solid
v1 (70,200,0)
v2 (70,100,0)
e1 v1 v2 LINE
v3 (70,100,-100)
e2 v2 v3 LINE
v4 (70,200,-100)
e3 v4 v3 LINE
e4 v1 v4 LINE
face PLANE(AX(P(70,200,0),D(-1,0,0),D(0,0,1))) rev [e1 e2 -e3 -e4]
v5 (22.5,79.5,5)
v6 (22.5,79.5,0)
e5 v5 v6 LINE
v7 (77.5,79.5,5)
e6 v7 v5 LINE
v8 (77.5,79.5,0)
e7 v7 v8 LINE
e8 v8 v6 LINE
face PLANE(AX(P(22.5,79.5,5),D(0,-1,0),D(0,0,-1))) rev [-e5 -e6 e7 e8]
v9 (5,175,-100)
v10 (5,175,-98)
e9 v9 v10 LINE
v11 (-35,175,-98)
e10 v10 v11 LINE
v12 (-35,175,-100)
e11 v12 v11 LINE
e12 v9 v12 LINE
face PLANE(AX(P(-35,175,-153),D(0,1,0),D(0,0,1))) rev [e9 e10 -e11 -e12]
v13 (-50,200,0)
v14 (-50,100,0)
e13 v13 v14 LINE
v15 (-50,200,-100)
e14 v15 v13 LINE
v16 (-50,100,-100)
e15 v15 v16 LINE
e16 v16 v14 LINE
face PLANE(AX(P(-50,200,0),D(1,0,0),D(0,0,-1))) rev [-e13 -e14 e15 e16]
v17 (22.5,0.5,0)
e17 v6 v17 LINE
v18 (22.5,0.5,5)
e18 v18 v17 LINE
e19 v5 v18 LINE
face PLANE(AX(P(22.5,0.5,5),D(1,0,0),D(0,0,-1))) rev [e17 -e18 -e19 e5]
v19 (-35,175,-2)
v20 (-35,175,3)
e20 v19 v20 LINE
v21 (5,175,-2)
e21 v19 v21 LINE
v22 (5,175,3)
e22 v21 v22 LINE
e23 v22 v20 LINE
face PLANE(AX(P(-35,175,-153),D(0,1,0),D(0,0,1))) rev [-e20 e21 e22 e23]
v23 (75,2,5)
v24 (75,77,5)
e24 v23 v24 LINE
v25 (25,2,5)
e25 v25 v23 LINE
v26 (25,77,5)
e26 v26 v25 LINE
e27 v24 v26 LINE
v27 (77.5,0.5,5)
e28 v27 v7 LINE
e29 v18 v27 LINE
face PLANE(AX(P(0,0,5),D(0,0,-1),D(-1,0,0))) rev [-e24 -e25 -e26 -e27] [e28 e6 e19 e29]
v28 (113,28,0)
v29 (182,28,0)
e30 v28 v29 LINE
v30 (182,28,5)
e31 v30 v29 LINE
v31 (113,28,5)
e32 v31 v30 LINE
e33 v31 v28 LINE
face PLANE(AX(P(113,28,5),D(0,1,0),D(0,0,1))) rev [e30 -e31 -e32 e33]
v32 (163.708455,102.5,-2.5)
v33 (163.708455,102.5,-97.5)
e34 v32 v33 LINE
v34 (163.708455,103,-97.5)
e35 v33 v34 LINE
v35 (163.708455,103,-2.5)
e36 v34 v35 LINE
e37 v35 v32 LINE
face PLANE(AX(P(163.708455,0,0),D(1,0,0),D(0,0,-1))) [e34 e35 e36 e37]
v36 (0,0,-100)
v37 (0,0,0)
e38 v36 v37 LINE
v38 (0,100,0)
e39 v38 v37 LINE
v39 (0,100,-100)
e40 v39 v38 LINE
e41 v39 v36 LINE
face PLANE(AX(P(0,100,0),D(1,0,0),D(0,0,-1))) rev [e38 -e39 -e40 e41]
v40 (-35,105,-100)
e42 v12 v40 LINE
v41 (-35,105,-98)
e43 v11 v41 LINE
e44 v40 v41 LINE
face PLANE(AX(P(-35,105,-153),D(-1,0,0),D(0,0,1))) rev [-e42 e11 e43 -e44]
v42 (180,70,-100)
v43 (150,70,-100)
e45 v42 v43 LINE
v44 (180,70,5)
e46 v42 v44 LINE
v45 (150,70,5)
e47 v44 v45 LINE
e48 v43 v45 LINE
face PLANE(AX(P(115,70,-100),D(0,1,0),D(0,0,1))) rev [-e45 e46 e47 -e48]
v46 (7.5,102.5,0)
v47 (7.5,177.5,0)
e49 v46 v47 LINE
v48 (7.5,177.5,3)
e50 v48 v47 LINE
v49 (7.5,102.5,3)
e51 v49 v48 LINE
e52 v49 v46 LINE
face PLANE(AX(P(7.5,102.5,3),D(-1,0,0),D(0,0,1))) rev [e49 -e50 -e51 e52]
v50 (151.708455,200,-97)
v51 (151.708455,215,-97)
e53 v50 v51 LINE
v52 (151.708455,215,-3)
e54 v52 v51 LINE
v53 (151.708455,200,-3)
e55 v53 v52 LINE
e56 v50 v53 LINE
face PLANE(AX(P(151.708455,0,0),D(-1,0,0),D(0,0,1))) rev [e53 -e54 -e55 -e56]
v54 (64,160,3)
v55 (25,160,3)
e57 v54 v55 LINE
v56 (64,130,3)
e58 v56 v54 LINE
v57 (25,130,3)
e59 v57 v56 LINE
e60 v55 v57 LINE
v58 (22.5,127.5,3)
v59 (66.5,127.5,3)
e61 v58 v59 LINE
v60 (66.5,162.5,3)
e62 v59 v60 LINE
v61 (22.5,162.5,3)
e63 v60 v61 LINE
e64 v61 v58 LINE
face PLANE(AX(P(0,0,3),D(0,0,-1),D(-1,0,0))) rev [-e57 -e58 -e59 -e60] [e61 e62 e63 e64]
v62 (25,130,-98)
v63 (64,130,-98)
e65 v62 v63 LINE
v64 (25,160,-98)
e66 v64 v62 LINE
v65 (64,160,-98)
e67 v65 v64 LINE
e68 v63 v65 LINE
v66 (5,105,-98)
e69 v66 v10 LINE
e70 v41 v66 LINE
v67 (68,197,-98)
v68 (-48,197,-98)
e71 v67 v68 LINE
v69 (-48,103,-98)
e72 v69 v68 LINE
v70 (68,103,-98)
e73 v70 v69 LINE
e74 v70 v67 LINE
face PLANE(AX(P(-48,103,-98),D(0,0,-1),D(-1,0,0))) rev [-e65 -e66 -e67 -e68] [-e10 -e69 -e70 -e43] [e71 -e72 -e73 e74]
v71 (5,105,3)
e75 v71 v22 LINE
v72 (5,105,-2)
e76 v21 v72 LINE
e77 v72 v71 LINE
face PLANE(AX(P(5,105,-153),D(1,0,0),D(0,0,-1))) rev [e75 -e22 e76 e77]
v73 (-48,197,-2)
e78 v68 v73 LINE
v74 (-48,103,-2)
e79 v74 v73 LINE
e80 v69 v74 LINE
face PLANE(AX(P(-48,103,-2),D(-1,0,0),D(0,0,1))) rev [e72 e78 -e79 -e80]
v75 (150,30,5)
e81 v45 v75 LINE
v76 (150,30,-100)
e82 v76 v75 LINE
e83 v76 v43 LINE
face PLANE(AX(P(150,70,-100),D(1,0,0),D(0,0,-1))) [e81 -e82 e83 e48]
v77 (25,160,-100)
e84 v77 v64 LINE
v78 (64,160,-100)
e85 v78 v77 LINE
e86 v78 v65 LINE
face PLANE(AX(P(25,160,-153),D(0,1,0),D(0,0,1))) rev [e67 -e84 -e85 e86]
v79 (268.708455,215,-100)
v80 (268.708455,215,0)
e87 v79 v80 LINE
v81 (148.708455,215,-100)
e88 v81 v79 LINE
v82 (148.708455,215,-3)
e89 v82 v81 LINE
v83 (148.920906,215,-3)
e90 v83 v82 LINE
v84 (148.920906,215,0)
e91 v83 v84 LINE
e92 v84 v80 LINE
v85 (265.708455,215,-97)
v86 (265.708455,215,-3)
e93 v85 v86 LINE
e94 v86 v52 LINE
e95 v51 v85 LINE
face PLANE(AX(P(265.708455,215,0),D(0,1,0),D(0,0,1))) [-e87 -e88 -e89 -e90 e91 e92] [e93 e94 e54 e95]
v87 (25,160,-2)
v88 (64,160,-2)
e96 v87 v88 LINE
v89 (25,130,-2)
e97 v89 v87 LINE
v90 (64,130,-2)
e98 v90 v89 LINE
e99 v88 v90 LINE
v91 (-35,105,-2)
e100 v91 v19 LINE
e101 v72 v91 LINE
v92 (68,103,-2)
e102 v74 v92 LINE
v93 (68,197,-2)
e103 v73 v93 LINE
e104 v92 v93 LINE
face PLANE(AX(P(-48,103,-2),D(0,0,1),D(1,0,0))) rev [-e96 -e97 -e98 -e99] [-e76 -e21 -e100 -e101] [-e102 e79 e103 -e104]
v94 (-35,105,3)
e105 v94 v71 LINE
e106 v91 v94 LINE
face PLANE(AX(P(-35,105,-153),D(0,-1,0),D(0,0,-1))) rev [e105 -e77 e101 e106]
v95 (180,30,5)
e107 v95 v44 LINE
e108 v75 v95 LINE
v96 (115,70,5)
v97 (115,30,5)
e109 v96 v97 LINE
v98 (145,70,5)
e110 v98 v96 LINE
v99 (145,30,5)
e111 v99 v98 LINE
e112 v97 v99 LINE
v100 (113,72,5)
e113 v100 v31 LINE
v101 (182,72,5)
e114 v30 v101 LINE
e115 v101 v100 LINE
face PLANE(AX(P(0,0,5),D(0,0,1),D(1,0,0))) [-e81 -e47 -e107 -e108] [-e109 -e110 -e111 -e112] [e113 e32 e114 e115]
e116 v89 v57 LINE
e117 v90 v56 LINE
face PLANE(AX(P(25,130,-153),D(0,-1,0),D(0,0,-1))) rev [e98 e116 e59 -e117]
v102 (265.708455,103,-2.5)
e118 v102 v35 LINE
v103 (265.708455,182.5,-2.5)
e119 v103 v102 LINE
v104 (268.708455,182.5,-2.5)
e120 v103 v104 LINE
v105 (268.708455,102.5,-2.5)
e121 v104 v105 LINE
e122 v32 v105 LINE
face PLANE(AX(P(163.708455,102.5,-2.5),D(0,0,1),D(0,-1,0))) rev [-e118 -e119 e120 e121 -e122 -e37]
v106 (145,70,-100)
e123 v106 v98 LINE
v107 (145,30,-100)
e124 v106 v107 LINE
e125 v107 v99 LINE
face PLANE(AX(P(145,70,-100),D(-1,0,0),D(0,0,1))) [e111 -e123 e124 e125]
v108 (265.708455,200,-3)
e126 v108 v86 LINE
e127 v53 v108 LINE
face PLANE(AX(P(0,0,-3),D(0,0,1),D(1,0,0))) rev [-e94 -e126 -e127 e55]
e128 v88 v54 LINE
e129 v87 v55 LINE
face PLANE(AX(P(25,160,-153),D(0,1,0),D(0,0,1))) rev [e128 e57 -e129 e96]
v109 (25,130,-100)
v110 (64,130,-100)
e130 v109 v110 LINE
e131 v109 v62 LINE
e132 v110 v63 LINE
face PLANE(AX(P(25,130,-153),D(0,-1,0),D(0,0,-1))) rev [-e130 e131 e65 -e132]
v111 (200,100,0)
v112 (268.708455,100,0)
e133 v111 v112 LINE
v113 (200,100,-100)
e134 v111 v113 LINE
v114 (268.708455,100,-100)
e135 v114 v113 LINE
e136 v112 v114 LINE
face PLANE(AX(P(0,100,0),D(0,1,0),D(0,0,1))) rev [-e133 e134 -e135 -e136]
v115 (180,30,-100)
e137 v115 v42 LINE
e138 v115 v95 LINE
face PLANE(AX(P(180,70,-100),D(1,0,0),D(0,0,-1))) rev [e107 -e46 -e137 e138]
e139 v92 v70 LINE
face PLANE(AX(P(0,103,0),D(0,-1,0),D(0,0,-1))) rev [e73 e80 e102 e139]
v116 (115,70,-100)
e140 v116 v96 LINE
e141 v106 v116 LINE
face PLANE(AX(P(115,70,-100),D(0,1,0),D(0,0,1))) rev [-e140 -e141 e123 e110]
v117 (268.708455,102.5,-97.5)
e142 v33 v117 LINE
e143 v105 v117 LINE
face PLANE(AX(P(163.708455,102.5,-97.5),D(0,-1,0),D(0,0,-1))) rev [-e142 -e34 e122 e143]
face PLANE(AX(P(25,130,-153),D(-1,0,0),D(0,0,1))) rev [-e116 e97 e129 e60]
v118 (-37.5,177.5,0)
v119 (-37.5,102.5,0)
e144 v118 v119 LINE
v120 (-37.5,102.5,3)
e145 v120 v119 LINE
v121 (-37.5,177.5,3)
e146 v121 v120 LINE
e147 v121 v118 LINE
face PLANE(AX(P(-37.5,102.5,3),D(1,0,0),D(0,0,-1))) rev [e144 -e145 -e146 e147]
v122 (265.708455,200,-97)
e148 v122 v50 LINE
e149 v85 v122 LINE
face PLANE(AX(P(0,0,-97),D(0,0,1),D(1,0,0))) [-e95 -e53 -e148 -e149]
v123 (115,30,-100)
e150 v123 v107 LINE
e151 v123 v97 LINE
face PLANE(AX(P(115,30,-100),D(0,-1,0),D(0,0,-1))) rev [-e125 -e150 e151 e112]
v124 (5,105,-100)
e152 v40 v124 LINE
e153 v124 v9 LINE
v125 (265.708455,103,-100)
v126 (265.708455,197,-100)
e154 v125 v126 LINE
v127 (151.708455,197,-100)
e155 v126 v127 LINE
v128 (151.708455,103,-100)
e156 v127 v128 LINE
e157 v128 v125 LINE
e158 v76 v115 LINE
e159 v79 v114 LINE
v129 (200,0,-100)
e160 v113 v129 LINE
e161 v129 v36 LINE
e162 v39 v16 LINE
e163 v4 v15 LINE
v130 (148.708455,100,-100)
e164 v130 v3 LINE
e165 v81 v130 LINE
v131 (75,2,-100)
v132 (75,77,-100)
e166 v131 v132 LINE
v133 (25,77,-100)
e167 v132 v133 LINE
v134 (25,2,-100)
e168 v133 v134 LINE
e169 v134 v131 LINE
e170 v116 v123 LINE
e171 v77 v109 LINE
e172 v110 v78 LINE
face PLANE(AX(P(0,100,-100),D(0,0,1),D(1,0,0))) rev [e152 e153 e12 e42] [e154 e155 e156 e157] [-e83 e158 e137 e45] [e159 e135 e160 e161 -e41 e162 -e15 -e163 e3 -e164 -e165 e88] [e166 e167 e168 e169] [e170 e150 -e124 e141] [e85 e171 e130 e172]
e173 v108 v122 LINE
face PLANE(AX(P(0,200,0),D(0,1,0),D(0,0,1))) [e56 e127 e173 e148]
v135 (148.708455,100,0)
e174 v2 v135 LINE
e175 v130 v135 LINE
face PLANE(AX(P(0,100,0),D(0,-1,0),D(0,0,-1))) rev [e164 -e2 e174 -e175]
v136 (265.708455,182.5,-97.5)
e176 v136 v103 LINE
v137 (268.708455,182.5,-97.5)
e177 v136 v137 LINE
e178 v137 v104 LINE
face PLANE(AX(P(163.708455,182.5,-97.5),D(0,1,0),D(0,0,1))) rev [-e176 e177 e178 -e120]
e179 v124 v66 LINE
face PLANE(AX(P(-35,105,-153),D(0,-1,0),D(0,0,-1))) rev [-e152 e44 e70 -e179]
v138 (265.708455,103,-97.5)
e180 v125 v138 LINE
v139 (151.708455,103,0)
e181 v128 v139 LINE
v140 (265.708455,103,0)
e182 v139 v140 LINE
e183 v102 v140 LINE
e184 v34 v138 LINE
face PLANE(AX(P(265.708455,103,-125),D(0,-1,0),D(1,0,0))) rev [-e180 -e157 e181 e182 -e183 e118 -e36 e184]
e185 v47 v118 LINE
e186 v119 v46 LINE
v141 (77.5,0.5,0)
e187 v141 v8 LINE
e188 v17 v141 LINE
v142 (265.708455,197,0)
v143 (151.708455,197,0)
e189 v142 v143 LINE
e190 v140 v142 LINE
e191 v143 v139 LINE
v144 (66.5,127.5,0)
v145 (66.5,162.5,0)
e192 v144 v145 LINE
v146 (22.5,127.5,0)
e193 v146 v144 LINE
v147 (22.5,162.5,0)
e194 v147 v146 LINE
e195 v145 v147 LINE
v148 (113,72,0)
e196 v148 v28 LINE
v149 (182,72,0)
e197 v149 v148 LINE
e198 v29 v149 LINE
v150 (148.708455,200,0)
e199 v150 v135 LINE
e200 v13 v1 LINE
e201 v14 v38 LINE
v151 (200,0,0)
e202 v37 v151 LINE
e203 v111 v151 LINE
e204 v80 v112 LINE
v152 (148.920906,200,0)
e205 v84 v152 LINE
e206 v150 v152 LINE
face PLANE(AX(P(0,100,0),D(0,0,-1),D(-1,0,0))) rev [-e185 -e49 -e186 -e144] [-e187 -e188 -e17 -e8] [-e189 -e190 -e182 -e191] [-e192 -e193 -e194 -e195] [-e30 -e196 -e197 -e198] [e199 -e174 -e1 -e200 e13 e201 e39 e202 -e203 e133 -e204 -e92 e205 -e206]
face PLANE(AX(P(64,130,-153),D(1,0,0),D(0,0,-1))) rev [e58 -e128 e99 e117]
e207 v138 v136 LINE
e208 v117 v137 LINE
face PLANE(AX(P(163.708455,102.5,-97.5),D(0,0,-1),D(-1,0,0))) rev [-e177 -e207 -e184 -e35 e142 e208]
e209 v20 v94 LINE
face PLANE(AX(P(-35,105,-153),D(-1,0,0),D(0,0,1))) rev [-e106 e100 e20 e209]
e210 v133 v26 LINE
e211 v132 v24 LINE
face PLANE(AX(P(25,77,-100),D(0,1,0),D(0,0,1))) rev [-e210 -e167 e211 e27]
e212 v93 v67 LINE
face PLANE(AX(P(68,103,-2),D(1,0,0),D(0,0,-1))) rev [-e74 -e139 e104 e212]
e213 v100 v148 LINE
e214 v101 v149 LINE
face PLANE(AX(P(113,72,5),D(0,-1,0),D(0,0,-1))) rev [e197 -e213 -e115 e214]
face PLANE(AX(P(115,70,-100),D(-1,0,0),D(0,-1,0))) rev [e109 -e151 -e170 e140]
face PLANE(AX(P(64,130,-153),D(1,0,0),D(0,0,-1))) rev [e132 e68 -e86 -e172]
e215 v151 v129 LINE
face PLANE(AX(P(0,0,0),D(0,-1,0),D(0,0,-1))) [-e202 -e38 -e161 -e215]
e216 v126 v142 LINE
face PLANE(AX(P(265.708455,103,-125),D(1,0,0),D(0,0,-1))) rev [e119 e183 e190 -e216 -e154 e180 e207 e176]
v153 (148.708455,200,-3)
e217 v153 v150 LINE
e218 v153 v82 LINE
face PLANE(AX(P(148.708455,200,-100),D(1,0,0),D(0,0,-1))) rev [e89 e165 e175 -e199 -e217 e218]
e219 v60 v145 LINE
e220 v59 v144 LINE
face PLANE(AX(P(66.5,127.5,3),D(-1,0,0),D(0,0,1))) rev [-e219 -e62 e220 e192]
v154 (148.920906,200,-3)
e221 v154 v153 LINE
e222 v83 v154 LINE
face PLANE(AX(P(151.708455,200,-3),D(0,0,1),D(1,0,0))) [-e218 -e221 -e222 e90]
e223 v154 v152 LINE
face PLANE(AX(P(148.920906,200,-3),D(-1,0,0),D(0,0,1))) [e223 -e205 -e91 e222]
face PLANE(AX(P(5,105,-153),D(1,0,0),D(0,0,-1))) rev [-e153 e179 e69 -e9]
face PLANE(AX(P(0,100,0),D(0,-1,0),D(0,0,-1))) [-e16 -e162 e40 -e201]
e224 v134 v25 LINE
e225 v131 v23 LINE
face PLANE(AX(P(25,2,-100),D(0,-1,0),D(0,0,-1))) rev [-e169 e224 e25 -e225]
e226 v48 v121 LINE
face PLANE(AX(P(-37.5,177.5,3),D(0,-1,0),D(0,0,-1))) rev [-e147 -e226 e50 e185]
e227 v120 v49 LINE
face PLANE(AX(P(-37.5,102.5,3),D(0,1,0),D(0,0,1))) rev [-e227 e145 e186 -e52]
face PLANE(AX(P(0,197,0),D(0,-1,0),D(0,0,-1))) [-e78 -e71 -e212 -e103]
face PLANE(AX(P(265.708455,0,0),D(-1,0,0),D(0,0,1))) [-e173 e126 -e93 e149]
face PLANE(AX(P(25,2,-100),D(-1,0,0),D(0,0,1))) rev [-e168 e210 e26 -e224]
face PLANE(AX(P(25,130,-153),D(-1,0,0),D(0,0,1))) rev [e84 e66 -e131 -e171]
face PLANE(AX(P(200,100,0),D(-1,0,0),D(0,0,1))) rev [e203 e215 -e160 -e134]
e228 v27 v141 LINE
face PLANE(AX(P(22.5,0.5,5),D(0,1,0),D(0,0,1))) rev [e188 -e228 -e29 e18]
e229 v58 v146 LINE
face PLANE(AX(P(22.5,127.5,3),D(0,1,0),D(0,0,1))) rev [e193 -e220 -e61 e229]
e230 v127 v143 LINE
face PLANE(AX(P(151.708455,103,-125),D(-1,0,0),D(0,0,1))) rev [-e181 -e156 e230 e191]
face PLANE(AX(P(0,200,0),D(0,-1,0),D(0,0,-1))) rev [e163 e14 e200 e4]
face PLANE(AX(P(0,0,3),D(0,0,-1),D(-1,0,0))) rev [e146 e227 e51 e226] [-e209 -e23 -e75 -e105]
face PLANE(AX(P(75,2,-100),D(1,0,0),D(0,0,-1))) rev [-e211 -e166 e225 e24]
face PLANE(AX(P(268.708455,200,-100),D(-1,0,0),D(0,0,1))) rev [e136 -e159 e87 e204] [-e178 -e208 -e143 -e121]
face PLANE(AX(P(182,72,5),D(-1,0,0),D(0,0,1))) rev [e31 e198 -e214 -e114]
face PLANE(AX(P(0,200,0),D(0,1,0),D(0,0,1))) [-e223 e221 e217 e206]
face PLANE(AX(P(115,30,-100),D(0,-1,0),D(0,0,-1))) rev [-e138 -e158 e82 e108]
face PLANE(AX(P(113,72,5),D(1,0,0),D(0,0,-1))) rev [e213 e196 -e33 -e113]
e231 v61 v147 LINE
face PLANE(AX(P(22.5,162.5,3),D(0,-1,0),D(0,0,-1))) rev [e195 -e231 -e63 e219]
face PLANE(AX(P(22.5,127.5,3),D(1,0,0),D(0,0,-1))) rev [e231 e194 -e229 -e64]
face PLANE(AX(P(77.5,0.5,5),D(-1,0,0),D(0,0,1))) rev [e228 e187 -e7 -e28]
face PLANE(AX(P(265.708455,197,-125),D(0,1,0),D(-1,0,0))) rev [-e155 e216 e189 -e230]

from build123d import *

# Parameters (mm, degrees)
BASE_BLOCK_SKETCH_W           = 200
BASE_BLOCK_SKETCH_H           = 100
BASE_BLOCK_DEPTH              = 100
UPPER_BLOCK_SKETCH_W          = 120
UPPER_BLOCK_SKETCH_H          = 100
UPPER_BLOCK_DEPTH             = 100
SIDE_ANNEX_DEPTH              = 100
FRONT_DOOR_OPENING_SKETCH_W   = 50
FRONT_DOOR_OPENING_SKETCH_H   = 75
FRONT_DOOR_OPENING_DEPTH      = 100
FRONT_WINDOW_OPENING_SKETCH_W = 65
FRONT_WINDOW_OPENING_SKETCH_H = 40
FRONT_WINDOW_OPENING_DEPTH    = 100
FRONT_WINDOW_MULLION_SKETCH_W = 5
FRONT_WINDOW_MULLION_SKETCH_H = 40
FRONT_WINDOW_MULLION_DEPTH    = 100
FRONT_WINDOW_FRAME_SKETCH_W   = 69
FRONT_WINDOW_FRAME_SKETCH_H   = 44
FRONT_WINDOW_FRAME_SKETCH_W_2 = 30
FRONT_WINDOW_FRAME_SKETCH_H_2 = 40
FRONT_WINDOW_FRAME_DEPTH      = 5
FRONT_DOOR_FRAME_SKETCH_W     = 55
FRONT_DOOR_FRAME_SKETCH_H     = 79
FRONT_DOOR_FRAME_SKETCH_W_2   = 50
FRONT_DOOR_FRAME_SKETCH_H_2   = 75
FRONT_DOOR_FRAME_DEPTH        = 5
UPPER_BLOCK_HOLLOW_SKETCH_W   = 114
UPPER_BLOCK_HOLLOW_SKETCH_H   = 94
UPPER_BLOCK_HOLLOW_DEPTH      = 125
UPPER_INTERIOR_CUT_SKETCH_W   = 95
UPPER_INTERIOR_CUT_SKETCH_H   = 80
UPPER_INTERIOR_CUT_DEPTH      = 105
UPPER_FRAME_MEMBER_1_SKETCH_W = 100
UPPER_FRAME_MEMBER_1_SKETCH_H = 15
UPPER_FRAME_MEMBER_1_DEPTH    = 3
UPPER_FRAME_MEMBER_2_SKETCH_W = 116.787548914
UPPER_FRAME_MEMBER_2_SKETCH_H = 15
UPPER_FRAME_MEMBER_2_DEPTH    = 3
UPPER_FRAME_MEMBER_3_SKETCH_W = 97
UPPER_FRAME_MEMBER_3_SKETCH_H = 15
UPPER_FRAME_MEMBER_3_DEPTH    = 3
UPPER_FRAME_MEMBER_4_SKETCH_W = 114
UPPER_FRAME_MEMBER_4_SKETCH_H = 15
UPPER_FRAME_MEMBER_4_DEPTH    = 3
ANNEX_DOOR_OPENING_SKETCH_W   = 40
ANNEX_DOOR_OPENING_SKETCH_H   = 70
ANNEX_DOOR_OPENING_DEPTH      = 153
ANNEX_WINDOW_OPENING_SKETCH_W = 39
ANNEX_WINDOW_OPENING_SKETCH_H = 30
ANNEX_WINDOW_OPENING_DEPTH    = 153
ANNEX_DOOR_FRAME_SKETCH_W     = 45
ANNEX_DOOR_FRAME_SKETCH_H     = 75
ANNEX_DOOR_FRAME_SKETCH_W_2   = 40
ANNEX_DOOR_FRAME_SKETCH_H_2   = 70
ANNEX_DOOR_FRAME_DEPTH        = 3
ANNEX_WINDOW_FRAME_SKETCH_W   = 44
ANNEX_WINDOW_FRAME_SKETCH_H   = 35
ANNEX_WINDOW_FRAME_SKETCH_W_2 = 39
ANNEX_WINDOW_FRAME_SKETCH_H_2 = 30
ANNEX_WINDOW_FRAME_DEPTH      = 3
ANNEX_HOLLOW_SKETCH_W         = 116
ANNEX_HOLLOW_SKETCH_H         = 96
ANNEX_HOLLOW_DEPTH            = 97
ANNEX_RIM_SKETCH_W            = 120
ANNEX_RIM_SKETCH_H            = 100
ANNEX_RIM_DEPTH               = 3


with BuildPart() as part:
    # Base Block Sketch → Base Block (new body)
    with BuildSketch(Plane(origin=(0, 0, 0), x_dir=(1, 0, 0), z_dir=(0, 1, 0))):
        with Locations((100, 50)):
            Rectangle(BASE_BLOCK_SKETCH_W, BASE_BLOCK_SKETCH_H)
    extrude(amount=BASE_BLOCK_DEPTH)

    # Upper Block Sketch → Upper Block (add)
    with BuildSketch(Plane(origin=(0, 100, 0), x_dir=(1, 0, 0), z_dir=(0, 1, 0))):
        with Locations((208.708454776, 50)):
            Rectangle(UPPER_BLOCK_SKETCH_W, UPPER_BLOCK_SKETCH_H)
    extrude(amount=UPPER_BLOCK_DEPTH)

    # Side Annex Sketch → Side Annex (add)
    with BuildSketch(Plane(origin=(0, 100, 0), x_dir=(1, 0, 0), z_dir=(0, 1, 0))):
        Polygon((0, 0), (70, 0), (70, 100), (0, 100), (-50, 100), (-50, 0), align=None)
    extrude(amount=SIDE_ANNEX_DEPTH)

    # Front Door Opening Sketch → Front Door Opening (cut)
    with BuildSketch(Plane.XY):
        with Locations((50, 39.5)):
            Rectangle(FRONT_DOOR_OPENING_SKETCH_W, FRONT_DOOR_OPENING_SKETCH_H)
    extrude(amount=-FRONT_DOOR_OPENING_DEPTH, mode=Mode.SUBTRACT)

    # Front Window Opening Sketch → Front Window Opening (cut)
    with BuildSketch(Plane.XY):
        with Locations((147.5, 50)):
            Rectangle(FRONT_WINDOW_OPENING_SKETCH_W, FRONT_WINDOW_OPENING_SKETCH_H)
    extrude(amount=-FRONT_WINDOW_OPENING_DEPTH, mode=Mode.SUBTRACT)

    # Front Window Mullion Sketch → Front Window Mullion (add)
    with BuildSketch(Plane.XY):
        with Locations((147.5, 50)):
            Rectangle(FRONT_WINDOW_MULLION_SKETCH_W, FRONT_WINDOW_MULLION_SKETCH_H)
    extrude(amount=-FRONT_WINDOW_MULLION_DEPTH)

    # Front Window Frame Sketch → Front Window Frame (add)
    with BuildSketch(Plane.XY):
        with Locations((147.5, 50)):
            Rectangle(FRONT_WINDOW_FRAME_SKETCH_W, FRONT_WINDOW_FRAME_SKETCH_H)
        with Locations((130, 50)):
            Rectangle(FRONT_WINDOW_FRAME_SKETCH_W_2, FRONT_WINDOW_FRAME_SKETCH_H_2, mode=Mode.SUBTRACT)
        with Locations((165, 50)):
            Rectangle(FRONT_WINDOW_FRAME_SKETCH_W_2, FRONT_WINDOW_FRAME_SKETCH_H_2, mode=Mode.SUBTRACT)
    extrude(amount=FRONT_WINDOW_FRAME_DEPTH)

    # Front Door Frame Sketch → Front Door Frame (add)
    with BuildSketch(Plane.XY):
        with Locations((50, 40)):
            Rectangle(FRONT_DOOR_FRAME_SKETCH_W, FRONT_DOOR_FRAME_SKETCH_H)
        with Locations((50, 39.5)):
            Rectangle(FRONT_DOOR_FRAME_SKETCH_W_2, FRONT_DOOR_FRAME_SKETCH_H_2, mode=Mode.SUBTRACT)
    extrude(amount=FRONT_DOOR_FRAME_DEPTH)

    # Upper Block Hollow Sketch → Upper Block Hollow (cut)
    with BuildSketch(Plane.XY):
        with Locations((208.708454776, 150)):
            Rectangle(UPPER_BLOCK_HOLLOW_SKETCH_W, UPPER_BLOCK_HOLLOW_SKETCH_H)
    extrude(amount=-UPPER_BLOCK_HOLLOW_DEPTH, mode=Mode.SUBTRACT)

    # Upper Interior Cut Sketch → Upper Interior Cut (cut)
    with BuildSketch(Plane(origin=(268.708454776, 0, 0), x_dir=(0, 0, -1), z_dir=(1, 0, 0))):
        with Locations((50, 142.5)):
            Rectangle(UPPER_INTERIOR_CUT_SKETCH_W, UPPER_INTERIOR_CUT_SKETCH_H)
    extrude(amount=-UPPER_INTERIOR_CUT_DEPTH, mode=Mode.SUBTRACT)

    # Upper Frame Member 1 Sketch → Upper Frame Member 1 (add)
    with BuildSketch(Plane(origin=(268.708454776, 0, 0), x_dir=(0, 0, -1), z_dir=(1, 0, 0))):
        with Locations((50, 207.5)):
            Rectangle(UPPER_FRAME_MEMBER_1_SKETCH_W, UPPER_FRAME_MEMBER_1_SKETCH_H)
    extrude(amount=-UPPER_FRAME_MEMBER_1_DEPTH)

    # Upper Frame Member 2 Sketch → Upper Frame Member 2 (add)
    with BuildSketch(Plane.XY):
        with Locations((207.314680319, 207.5)):
            Rectangle(UPPER_FRAME_MEMBER_2_SKETCH_W, UPPER_FRAME_MEMBER_2_SKETCH_H)
    extrude(amount=-UPPER_FRAME_MEMBER_2_DEPTH)

    # Upper Frame Member 3 Sketch → Upper Frame Member 3 (add)
    with BuildSketch(Plane.ZY.offset(-148.708454776)):
        with Locations((-51.5, 207.5)):
            Rectangle(UPPER_FRAME_MEMBER_3_SKETCH_W, UPPER_FRAME_MEMBER_3_SKETCH_H)
    extrude(amount=-UPPER_FRAME_MEMBER_3_DEPTH)

    # Upper Frame Member 4 Sketch → Upper Frame Member 4 (add)
    with BuildSketch(Plane(origin=(0, 0, -100), x_dir=(-1, 0, 0), z_dir=(0, 0, -1))):
        with Locations((-208.708454776, 207.5)):
            Rectangle(UPPER_FRAME_MEMBER_4_SKETCH_W, UPPER_FRAME_MEMBER_4_SKETCH_H)
    extrude(amount=-UPPER_FRAME_MEMBER_4_DEPTH)

    # Annex Door Opening Sketch → Annex Door Opening (cut)
    with BuildSketch(Plane.XY):
        with Locations((-15, 140)):
            Rectangle(ANNEX_DOOR_OPENING_SKETCH_W, ANNEX_DOOR_OPENING_SKETCH_H)
    extrude(amount=-ANNEX_DOOR_OPENING_DEPTH, mode=Mode.SUBTRACT)

    # Annex Window Opening Sketch → Annex Window Opening (cut)
    with BuildSketch(Plane.XY):
        with Locations((44.5, 145)):
            Rectangle(ANNEX_WINDOW_OPENING_SKETCH_W, ANNEX_WINDOW_OPENING_SKETCH_H)
    extrude(amount=-ANNEX_WINDOW_OPENING_DEPTH, mode=Mode.SUBTRACT)

    # Annex Door Frame Sketch → Annex Door Frame (add)
    with BuildSketch(Plane.XY):
        with Locations((-15, 140)):
            Rectangle(ANNEX_DOOR_FRAME_SKETCH_W, ANNEX_DOOR_FRAME_SKETCH_H)
        with Locations((-15, 140)):
            Rectangle(ANNEX_DOOR_FRAME_SKETCH_W_2, ANNEX_DOOR_FRAME_SKETCH_H_2, mode=Mode.SUBTRACT)
    extrude(amount=ANNEX_DOOR_FRAME_DEPTH)

    # Annex Window Frame Sketch → Annex Window Frame (add)
    with BuildSketch(Plane.XY):
        with Locations((44.5, 145)):
            Rectangle(ANNEX_WINDOW_FRAME_SKETCH_W, ANNEX_WINDOW_FRAME_SKETCH_H)
        with Locations((44.5, 145)):
            Rectangle(ANNEX_WINDOW_FRAME_SKETCH_W_2, ANNEX_WINDOW_FRAME_SKETCH_H_2, mode=Mode.SUBTRACT)
    extrude(amount=ANNEX_WINDOW_FRAME_DEPTH)

    # Annex Hollow Sketch → Annex Hollow (cut)
    with BuildSketch(Plane(origin=(0, 200, 0), x_dir=(1, 0, 0), z_dir=(0, 1, 0))):
        with Locations((10, 50)):
            Rectangle(ANNEX_HOLLOW_SKETCH_W, ANNEX_HOLLOW_SKETCH_H)
    extrude(amount=-ANNEX_HOLLOW_DEPTH, mode=Mode.SUBTRACT)

    # Annex Rim Sketch → Annex Rim (add)
    with BuildSketch(Plane(origin=(0, 200, 0), x_dir=(1, 0, 0), z_dir=(0, 1, 0))):
        with Locations((10, 50)):
            Rectangle(ANNEX_RIM_SKETCH_W, ANNEX_RIM_SKETCH_H)
    extrude(amount=-ANNEX_RIM_DEPTH)


solid = part.part
